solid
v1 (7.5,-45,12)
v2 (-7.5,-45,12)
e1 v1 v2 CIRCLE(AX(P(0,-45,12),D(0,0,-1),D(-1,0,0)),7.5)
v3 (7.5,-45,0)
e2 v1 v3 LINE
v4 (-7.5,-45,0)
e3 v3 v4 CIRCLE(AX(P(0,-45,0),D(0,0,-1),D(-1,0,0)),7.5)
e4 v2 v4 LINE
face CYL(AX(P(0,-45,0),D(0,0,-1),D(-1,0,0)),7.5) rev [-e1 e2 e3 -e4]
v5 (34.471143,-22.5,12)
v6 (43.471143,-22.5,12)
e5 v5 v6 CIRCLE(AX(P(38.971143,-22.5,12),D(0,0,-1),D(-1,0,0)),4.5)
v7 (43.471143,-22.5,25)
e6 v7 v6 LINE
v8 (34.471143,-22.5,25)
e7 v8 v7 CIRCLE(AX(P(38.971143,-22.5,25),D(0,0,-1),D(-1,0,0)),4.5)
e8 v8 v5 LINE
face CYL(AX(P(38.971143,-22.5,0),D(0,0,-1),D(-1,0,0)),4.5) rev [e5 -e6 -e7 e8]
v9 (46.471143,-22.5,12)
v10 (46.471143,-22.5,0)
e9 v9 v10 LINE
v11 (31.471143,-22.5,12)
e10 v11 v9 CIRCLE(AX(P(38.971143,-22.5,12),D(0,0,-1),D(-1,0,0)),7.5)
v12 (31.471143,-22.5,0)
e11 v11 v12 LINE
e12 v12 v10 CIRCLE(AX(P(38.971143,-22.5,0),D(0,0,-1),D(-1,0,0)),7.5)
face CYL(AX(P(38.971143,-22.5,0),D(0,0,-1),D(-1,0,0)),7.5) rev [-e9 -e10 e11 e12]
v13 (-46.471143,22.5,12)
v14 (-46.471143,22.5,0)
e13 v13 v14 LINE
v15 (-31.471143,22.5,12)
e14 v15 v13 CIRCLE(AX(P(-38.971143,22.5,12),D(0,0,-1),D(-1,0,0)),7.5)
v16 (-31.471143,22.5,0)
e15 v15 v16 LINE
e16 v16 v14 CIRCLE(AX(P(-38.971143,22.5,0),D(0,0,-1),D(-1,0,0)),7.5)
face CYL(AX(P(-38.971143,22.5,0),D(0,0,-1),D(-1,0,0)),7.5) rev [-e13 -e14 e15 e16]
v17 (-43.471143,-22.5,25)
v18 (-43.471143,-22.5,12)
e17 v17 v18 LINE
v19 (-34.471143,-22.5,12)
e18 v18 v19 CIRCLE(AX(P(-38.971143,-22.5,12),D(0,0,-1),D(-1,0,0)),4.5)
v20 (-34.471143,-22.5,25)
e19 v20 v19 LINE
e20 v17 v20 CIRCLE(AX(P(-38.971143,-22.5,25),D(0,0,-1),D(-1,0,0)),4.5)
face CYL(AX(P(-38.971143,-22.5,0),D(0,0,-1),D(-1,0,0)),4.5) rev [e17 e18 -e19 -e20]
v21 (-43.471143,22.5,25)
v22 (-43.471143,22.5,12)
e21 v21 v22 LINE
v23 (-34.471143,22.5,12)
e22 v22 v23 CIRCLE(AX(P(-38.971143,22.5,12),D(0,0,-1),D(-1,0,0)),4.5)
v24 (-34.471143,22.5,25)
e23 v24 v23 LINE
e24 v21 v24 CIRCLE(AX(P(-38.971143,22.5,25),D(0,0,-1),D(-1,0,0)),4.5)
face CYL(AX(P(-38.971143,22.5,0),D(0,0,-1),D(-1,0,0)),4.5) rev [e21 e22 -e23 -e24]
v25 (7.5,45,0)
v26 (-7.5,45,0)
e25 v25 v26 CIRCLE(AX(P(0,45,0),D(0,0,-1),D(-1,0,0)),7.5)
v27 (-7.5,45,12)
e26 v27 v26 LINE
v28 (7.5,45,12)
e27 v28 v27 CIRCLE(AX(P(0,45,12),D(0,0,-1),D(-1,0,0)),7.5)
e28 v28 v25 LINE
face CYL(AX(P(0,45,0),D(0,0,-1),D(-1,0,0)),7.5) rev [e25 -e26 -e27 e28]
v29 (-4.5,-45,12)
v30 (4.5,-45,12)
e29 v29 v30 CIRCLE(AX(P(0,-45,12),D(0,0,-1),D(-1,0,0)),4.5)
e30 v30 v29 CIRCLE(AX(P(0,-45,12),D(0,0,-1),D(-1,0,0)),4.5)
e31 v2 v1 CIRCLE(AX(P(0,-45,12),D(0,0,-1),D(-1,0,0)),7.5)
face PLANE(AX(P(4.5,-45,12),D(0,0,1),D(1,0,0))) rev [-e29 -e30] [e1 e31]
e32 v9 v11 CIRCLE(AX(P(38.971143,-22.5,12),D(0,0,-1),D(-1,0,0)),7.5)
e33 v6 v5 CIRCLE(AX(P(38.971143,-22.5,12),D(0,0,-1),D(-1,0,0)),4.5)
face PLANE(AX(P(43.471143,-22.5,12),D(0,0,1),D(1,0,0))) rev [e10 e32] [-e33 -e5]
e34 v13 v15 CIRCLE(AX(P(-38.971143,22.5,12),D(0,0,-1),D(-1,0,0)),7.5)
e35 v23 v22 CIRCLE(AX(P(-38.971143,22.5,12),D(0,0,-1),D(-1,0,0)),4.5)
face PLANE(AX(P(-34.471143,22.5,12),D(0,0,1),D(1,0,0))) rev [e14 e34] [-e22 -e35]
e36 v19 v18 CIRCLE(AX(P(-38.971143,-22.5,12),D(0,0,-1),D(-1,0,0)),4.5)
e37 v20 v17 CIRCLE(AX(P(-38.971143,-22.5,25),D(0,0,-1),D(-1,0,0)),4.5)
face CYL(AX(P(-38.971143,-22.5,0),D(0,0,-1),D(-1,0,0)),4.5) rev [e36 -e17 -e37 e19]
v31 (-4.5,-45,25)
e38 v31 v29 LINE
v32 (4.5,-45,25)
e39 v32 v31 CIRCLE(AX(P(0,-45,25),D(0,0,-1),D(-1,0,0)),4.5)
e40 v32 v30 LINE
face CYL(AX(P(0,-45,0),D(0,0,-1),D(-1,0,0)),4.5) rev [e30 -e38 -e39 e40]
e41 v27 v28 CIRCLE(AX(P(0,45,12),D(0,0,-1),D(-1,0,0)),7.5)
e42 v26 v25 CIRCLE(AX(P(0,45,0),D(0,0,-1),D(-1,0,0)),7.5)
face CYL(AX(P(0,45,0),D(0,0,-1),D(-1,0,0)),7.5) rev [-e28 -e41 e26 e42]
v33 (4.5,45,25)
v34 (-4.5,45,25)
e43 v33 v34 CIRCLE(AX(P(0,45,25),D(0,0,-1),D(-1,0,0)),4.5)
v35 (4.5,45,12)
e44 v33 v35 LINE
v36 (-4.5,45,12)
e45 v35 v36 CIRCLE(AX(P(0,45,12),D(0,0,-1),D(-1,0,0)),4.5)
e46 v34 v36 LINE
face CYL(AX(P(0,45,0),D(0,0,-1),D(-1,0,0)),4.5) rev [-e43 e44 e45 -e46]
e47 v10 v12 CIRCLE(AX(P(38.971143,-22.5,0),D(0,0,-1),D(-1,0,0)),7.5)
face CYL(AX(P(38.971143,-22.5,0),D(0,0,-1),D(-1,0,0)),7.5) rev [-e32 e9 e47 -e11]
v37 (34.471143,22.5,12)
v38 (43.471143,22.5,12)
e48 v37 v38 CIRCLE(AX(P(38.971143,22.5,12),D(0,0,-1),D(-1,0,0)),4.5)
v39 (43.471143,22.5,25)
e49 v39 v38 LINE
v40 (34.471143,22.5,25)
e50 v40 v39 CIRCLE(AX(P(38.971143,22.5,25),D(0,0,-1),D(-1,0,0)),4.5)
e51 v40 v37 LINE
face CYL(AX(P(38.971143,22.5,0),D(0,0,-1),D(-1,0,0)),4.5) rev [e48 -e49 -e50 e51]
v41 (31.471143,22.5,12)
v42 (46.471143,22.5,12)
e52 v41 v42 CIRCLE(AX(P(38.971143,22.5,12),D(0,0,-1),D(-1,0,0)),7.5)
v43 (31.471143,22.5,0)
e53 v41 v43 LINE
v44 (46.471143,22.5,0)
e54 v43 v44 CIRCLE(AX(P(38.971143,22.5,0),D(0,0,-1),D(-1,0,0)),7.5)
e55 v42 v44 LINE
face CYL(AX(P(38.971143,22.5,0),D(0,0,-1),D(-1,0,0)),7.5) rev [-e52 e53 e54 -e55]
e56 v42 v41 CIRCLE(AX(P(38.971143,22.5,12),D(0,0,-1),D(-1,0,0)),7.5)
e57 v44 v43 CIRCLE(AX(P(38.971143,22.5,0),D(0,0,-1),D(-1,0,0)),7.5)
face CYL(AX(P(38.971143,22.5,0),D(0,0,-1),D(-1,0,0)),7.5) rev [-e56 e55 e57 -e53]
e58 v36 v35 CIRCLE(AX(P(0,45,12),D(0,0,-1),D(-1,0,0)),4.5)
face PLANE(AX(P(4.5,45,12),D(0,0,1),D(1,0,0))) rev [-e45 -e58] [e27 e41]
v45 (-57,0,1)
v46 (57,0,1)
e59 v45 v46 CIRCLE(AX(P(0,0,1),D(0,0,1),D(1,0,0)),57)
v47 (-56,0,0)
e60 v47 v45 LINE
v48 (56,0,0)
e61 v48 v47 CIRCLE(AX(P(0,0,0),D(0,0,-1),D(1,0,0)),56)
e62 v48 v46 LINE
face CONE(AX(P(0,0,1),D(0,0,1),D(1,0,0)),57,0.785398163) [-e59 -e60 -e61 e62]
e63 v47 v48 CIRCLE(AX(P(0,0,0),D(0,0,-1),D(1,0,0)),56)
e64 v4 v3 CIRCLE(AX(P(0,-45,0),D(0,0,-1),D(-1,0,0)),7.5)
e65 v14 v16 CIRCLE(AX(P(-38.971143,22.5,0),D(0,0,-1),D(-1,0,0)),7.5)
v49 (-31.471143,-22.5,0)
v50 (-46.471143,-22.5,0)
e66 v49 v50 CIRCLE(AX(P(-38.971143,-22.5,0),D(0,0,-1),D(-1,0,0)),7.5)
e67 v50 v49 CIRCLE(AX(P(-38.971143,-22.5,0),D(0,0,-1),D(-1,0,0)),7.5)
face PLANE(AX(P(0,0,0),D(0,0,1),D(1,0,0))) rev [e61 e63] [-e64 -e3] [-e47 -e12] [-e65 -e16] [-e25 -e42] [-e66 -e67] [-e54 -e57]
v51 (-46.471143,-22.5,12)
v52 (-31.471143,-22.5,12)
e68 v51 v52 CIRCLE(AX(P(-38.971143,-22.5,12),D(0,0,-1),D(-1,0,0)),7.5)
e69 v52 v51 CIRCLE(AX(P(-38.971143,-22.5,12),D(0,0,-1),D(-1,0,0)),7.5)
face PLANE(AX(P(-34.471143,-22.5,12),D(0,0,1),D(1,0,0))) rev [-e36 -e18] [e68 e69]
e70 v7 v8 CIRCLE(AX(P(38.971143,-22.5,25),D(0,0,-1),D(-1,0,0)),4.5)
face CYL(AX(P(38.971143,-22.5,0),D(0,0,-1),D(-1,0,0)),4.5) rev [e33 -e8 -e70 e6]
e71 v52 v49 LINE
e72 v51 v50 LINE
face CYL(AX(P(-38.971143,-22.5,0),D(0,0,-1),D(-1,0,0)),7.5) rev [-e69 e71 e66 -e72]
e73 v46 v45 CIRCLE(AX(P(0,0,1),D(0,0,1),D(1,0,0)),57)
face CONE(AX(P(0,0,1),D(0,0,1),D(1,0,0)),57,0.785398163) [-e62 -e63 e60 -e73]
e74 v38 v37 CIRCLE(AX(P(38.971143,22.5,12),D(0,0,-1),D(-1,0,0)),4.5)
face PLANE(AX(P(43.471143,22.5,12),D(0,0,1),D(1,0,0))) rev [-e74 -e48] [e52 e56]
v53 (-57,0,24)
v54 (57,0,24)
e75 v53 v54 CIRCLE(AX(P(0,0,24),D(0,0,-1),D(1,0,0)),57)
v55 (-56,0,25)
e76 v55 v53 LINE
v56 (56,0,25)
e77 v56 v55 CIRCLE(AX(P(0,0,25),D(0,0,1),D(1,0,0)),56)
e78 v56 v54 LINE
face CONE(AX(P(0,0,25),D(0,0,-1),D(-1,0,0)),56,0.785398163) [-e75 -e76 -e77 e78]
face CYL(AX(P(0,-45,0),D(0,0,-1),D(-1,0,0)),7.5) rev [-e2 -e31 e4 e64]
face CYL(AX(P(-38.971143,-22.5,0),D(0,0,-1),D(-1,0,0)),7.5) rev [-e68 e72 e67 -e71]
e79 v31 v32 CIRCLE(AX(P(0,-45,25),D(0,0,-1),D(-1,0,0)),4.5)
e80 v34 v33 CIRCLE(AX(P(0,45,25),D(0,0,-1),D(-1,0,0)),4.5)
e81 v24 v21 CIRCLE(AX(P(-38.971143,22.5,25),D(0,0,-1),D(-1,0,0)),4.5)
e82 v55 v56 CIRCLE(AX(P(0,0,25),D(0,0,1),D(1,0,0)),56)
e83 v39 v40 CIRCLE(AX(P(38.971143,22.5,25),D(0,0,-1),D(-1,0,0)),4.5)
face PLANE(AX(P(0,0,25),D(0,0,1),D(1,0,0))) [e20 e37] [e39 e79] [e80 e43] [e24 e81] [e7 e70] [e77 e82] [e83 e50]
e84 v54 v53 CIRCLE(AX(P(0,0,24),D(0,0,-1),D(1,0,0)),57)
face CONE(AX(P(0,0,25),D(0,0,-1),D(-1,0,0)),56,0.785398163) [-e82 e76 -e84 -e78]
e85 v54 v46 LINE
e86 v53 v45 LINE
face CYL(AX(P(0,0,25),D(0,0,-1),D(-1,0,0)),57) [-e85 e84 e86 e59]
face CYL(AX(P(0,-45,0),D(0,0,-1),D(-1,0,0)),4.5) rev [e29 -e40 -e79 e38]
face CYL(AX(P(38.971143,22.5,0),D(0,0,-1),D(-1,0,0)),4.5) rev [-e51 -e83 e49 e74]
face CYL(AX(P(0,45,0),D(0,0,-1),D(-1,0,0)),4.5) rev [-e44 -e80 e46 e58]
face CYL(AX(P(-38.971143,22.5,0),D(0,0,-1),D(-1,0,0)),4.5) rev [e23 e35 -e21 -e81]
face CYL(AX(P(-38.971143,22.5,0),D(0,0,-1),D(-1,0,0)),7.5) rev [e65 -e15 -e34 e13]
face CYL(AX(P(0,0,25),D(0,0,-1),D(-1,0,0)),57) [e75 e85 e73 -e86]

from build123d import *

# Parameters (mm, degrees)
SKETCH1_R                                           = 57
BOSS_EXTRUDE1_DEPTH                                 = 25
CHAMFER3_SIZE                                       = 1
HOLE_SIZE_PER_SOCKET_HEAD_CAP_SCREW_TYP_D           = 9
HOLE_SIZE_PER_SOCKET_HEAD_CAP_SCREW_TYP_CBORE_D     = 15
HOLE_SIZE_PER_SOCKET_HEAD_CAP_SCREW_TYP_CBORE_DEPTH = 12
CIRPATTERN1_COUNT                                   = 6


with BuildPart() as part:
    # Sketch1 → Boss-Extrude1 (new body)
    with BuildSketch(Plane.XY):
        Circle(SKETCH1_R)
    extrude(amount=BOSS_EXTRUDE1_DEPTH)

    # Chamfer3
    chamfer3_edges = [part.edges().sort_by_distance(p)[0] for p in [
        (-57, 0, 0),
        (-57, 0, 25),
    ]]
    chamfer(chamfer3_edges, length=CHAMFER3_SIZE)

    # Hole size (per socket head cap screw type)1 (through all)
    with Locations(Plane(origin=(0, 0, 0), x_dir=(-1, 0, 0), z_dir=(0, 0, -1))):
        with Locations((0, 45)):
            hole_size_per_socket_head_cap_screw_typ = CounterBoreHole(HOLE_SIZE_PER_SOCKET_HEAD_CAP_SCREW_TYP_D / 2, HOLE_SIZE_PER_SOCKET_HEAD_CAP_SCREW_TYP_CBORE_D / 2, HOLE_SIZE_PER_SOCKET_HEAD_CAP_SCREW_TYP_CBORE_DEPTH)

    # CirPattern1: Hole size (per socket head cap screw type)1 ×6 about axis
    cirpattern1_axis = Axis((0, 0, 0), (0, 0, 1))
    for i in range(1, CIRPATTERN1_COUNT):
        add(hole_size_per_socket_head_cap_screw_typ.rotate(cirpattern1_axis, i * 360 / CIRPATTERN1_COUNT), mode=Mode.SUBTRACT)


solid = part.part
